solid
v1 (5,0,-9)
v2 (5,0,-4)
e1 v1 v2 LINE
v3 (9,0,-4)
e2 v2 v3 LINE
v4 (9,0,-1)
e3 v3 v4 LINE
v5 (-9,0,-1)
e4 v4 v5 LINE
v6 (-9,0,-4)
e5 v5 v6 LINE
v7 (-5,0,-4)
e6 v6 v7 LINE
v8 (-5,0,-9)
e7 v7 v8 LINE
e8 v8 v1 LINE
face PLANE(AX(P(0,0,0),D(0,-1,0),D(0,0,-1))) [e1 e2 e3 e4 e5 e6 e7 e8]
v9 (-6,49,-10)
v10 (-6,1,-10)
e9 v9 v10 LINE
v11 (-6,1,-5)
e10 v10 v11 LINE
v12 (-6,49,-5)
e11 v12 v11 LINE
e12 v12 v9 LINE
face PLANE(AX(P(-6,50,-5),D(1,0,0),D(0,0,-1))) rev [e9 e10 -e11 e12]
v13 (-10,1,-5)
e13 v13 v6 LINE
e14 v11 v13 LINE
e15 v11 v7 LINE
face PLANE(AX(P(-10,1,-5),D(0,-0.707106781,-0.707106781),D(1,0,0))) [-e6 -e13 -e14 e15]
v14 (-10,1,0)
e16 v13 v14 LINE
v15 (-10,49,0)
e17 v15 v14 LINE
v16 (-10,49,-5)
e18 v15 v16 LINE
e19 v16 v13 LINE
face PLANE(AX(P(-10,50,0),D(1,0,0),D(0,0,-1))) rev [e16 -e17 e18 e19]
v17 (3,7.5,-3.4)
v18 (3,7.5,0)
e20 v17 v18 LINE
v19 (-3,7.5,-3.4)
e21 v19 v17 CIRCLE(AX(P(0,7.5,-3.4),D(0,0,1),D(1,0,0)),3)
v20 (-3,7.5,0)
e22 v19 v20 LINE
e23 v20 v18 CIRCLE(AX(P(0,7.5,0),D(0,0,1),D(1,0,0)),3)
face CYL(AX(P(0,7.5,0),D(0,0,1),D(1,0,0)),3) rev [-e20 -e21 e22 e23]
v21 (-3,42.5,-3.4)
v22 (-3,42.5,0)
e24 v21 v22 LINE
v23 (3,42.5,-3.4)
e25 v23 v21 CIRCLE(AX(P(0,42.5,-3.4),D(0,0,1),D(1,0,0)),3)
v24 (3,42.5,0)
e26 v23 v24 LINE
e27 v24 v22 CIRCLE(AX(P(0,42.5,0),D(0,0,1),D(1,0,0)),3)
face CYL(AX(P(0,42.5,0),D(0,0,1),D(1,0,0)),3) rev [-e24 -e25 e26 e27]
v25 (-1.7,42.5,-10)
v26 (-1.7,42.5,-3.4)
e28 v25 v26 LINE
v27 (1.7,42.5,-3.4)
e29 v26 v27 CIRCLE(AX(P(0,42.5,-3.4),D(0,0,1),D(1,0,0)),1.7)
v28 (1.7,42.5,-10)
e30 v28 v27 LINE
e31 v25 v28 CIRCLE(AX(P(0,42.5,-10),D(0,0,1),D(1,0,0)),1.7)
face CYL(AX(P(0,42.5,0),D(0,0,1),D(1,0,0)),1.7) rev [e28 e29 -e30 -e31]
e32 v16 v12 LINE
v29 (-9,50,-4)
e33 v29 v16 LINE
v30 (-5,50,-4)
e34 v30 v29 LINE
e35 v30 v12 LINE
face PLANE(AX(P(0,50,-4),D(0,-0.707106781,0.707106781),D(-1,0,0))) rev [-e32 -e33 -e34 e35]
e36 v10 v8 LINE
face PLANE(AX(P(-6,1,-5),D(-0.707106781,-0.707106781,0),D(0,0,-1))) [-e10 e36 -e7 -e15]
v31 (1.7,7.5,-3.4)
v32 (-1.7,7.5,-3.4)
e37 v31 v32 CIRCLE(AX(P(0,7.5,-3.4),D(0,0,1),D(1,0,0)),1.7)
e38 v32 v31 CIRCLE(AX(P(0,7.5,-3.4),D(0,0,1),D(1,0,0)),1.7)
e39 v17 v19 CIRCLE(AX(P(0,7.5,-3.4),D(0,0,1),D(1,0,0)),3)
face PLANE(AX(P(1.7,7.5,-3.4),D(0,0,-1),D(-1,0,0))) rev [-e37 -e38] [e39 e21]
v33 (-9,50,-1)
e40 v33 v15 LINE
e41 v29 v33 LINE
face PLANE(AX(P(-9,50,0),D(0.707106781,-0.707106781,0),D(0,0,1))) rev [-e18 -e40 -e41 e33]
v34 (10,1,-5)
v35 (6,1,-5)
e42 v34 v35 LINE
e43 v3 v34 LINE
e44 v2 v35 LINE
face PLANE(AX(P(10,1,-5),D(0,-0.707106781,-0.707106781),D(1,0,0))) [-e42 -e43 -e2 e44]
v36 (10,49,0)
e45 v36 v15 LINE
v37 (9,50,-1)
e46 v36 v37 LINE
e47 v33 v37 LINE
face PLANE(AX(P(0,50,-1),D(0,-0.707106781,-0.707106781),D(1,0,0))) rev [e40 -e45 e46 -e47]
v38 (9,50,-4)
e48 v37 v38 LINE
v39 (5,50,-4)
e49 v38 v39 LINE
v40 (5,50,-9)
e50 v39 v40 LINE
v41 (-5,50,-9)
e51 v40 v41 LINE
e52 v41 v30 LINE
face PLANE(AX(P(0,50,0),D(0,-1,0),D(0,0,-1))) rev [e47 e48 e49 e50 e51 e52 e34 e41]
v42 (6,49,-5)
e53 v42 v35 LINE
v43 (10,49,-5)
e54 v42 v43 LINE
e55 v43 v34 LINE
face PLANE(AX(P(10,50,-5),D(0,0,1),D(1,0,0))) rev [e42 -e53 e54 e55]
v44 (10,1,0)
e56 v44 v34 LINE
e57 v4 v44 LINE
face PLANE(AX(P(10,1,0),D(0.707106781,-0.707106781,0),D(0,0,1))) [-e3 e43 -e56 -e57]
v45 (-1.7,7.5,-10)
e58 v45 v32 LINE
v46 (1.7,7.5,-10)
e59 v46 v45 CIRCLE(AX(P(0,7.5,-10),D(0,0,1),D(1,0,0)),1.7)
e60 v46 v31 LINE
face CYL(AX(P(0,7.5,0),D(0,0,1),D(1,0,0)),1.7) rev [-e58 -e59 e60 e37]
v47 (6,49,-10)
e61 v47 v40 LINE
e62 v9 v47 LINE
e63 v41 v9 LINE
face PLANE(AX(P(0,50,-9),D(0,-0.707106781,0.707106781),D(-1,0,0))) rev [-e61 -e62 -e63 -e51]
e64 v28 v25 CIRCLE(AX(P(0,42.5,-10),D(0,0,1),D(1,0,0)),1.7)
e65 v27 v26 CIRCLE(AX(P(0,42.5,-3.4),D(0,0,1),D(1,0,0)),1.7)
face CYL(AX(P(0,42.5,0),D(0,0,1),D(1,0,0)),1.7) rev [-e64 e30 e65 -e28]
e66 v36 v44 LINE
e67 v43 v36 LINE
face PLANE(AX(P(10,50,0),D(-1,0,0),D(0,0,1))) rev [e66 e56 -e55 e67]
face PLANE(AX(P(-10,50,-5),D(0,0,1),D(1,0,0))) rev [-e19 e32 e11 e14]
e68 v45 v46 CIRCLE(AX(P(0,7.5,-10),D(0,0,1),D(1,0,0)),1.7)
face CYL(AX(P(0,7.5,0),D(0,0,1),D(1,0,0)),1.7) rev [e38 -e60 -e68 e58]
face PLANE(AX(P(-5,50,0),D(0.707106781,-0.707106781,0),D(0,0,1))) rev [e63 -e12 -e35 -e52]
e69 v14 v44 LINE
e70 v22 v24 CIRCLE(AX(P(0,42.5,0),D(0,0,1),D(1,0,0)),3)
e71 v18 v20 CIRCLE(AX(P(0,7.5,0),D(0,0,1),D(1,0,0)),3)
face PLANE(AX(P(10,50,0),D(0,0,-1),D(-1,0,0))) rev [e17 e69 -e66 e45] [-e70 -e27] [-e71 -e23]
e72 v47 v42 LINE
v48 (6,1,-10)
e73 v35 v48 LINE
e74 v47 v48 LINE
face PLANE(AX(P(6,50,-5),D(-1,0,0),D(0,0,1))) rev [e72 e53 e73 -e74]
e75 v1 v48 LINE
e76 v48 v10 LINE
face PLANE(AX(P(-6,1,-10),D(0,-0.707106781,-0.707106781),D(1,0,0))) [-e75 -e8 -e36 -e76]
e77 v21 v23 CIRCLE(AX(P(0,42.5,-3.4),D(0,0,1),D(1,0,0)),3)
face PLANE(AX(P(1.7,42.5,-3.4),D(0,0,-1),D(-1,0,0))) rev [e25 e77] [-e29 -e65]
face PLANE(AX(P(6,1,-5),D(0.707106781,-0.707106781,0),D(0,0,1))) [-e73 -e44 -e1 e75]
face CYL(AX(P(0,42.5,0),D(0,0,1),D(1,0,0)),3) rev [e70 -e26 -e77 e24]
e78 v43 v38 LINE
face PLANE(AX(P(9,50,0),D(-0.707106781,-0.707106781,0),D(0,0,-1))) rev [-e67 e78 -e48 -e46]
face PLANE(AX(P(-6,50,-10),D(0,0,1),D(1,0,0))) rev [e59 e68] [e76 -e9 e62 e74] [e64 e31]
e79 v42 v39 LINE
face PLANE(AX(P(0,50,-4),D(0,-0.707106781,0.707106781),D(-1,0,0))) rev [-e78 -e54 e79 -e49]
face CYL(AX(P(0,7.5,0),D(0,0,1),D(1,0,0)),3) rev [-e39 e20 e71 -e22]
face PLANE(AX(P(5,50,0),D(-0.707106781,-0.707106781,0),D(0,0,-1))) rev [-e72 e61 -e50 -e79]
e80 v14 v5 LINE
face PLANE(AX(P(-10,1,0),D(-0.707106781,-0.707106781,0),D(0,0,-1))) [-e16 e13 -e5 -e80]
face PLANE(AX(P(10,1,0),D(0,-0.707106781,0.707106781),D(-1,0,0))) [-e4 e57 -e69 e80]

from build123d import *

# Parameters (mm, degrees)
EXTRUDE_1_DEPTH              = 50
CHAMFER_1_SIZE               = 1
HOLE_WIZARD_M3_1_D           = 3.4
HOLE_WIZARD_M3_1_CBORE_D     = 6
HOLE_WIZARD_M3_1_CBORE_DEPTH = 3.4


with BuildPart() as part:
    # 草图1 → 凸台-拉伸1 (new body)
    with BuildSketch(Plane(origin=(0, 0, 0), x_dir=(1, 0, 0), z_dir=(0, 1, 0))):
        Polygon((10, 0), (-10, 0), (-10, 5), (-6, 5), (-6, 10), (6, 10), (6, 5), (10, 5), align=None)
    extrude(amount=EXTRUDE_1_DEPTH)

    # 倒角1
    chamfer_1_edges = [part.edges().sort_by_distance(p)[0] for p in [
        (8, 0, -5),
        (10, 0, -2.5),
        (0, 0, 0),
        (-10, 0, -2.5),
        (10, 50, -2.5),
        (8, 50, -5),
        (6, 50, -7.5),
        (0, 50, -10),
        (-6, 50, -7.5),
        (-8, 50, -5),
        (-10, 50, -2.5),
        (-8, 0, -5),
        (0, 50, 0),
        (-6, 0, -7.5),
        (0, 0, -10),
        (6, 0, -7.5),
    ]]
    chamfer(chamfer_1_edges, length=CHAMFER_1_SIZE)

    # M3 六角圆柱头螺钉的柱形沉头孔1 (through all)
    with Locations(Plane.XY):
        with Locations((0, 42.5), (0, 7.5)):
            CounterBoreHole(HOLE_WIZARD_M3_1_D / 2, HOLE_WIZARD_M3_1_CBORE_D / 2, HOLE_WIZARD_M3_1_CBORE_DEPTH)


solid = part.part
